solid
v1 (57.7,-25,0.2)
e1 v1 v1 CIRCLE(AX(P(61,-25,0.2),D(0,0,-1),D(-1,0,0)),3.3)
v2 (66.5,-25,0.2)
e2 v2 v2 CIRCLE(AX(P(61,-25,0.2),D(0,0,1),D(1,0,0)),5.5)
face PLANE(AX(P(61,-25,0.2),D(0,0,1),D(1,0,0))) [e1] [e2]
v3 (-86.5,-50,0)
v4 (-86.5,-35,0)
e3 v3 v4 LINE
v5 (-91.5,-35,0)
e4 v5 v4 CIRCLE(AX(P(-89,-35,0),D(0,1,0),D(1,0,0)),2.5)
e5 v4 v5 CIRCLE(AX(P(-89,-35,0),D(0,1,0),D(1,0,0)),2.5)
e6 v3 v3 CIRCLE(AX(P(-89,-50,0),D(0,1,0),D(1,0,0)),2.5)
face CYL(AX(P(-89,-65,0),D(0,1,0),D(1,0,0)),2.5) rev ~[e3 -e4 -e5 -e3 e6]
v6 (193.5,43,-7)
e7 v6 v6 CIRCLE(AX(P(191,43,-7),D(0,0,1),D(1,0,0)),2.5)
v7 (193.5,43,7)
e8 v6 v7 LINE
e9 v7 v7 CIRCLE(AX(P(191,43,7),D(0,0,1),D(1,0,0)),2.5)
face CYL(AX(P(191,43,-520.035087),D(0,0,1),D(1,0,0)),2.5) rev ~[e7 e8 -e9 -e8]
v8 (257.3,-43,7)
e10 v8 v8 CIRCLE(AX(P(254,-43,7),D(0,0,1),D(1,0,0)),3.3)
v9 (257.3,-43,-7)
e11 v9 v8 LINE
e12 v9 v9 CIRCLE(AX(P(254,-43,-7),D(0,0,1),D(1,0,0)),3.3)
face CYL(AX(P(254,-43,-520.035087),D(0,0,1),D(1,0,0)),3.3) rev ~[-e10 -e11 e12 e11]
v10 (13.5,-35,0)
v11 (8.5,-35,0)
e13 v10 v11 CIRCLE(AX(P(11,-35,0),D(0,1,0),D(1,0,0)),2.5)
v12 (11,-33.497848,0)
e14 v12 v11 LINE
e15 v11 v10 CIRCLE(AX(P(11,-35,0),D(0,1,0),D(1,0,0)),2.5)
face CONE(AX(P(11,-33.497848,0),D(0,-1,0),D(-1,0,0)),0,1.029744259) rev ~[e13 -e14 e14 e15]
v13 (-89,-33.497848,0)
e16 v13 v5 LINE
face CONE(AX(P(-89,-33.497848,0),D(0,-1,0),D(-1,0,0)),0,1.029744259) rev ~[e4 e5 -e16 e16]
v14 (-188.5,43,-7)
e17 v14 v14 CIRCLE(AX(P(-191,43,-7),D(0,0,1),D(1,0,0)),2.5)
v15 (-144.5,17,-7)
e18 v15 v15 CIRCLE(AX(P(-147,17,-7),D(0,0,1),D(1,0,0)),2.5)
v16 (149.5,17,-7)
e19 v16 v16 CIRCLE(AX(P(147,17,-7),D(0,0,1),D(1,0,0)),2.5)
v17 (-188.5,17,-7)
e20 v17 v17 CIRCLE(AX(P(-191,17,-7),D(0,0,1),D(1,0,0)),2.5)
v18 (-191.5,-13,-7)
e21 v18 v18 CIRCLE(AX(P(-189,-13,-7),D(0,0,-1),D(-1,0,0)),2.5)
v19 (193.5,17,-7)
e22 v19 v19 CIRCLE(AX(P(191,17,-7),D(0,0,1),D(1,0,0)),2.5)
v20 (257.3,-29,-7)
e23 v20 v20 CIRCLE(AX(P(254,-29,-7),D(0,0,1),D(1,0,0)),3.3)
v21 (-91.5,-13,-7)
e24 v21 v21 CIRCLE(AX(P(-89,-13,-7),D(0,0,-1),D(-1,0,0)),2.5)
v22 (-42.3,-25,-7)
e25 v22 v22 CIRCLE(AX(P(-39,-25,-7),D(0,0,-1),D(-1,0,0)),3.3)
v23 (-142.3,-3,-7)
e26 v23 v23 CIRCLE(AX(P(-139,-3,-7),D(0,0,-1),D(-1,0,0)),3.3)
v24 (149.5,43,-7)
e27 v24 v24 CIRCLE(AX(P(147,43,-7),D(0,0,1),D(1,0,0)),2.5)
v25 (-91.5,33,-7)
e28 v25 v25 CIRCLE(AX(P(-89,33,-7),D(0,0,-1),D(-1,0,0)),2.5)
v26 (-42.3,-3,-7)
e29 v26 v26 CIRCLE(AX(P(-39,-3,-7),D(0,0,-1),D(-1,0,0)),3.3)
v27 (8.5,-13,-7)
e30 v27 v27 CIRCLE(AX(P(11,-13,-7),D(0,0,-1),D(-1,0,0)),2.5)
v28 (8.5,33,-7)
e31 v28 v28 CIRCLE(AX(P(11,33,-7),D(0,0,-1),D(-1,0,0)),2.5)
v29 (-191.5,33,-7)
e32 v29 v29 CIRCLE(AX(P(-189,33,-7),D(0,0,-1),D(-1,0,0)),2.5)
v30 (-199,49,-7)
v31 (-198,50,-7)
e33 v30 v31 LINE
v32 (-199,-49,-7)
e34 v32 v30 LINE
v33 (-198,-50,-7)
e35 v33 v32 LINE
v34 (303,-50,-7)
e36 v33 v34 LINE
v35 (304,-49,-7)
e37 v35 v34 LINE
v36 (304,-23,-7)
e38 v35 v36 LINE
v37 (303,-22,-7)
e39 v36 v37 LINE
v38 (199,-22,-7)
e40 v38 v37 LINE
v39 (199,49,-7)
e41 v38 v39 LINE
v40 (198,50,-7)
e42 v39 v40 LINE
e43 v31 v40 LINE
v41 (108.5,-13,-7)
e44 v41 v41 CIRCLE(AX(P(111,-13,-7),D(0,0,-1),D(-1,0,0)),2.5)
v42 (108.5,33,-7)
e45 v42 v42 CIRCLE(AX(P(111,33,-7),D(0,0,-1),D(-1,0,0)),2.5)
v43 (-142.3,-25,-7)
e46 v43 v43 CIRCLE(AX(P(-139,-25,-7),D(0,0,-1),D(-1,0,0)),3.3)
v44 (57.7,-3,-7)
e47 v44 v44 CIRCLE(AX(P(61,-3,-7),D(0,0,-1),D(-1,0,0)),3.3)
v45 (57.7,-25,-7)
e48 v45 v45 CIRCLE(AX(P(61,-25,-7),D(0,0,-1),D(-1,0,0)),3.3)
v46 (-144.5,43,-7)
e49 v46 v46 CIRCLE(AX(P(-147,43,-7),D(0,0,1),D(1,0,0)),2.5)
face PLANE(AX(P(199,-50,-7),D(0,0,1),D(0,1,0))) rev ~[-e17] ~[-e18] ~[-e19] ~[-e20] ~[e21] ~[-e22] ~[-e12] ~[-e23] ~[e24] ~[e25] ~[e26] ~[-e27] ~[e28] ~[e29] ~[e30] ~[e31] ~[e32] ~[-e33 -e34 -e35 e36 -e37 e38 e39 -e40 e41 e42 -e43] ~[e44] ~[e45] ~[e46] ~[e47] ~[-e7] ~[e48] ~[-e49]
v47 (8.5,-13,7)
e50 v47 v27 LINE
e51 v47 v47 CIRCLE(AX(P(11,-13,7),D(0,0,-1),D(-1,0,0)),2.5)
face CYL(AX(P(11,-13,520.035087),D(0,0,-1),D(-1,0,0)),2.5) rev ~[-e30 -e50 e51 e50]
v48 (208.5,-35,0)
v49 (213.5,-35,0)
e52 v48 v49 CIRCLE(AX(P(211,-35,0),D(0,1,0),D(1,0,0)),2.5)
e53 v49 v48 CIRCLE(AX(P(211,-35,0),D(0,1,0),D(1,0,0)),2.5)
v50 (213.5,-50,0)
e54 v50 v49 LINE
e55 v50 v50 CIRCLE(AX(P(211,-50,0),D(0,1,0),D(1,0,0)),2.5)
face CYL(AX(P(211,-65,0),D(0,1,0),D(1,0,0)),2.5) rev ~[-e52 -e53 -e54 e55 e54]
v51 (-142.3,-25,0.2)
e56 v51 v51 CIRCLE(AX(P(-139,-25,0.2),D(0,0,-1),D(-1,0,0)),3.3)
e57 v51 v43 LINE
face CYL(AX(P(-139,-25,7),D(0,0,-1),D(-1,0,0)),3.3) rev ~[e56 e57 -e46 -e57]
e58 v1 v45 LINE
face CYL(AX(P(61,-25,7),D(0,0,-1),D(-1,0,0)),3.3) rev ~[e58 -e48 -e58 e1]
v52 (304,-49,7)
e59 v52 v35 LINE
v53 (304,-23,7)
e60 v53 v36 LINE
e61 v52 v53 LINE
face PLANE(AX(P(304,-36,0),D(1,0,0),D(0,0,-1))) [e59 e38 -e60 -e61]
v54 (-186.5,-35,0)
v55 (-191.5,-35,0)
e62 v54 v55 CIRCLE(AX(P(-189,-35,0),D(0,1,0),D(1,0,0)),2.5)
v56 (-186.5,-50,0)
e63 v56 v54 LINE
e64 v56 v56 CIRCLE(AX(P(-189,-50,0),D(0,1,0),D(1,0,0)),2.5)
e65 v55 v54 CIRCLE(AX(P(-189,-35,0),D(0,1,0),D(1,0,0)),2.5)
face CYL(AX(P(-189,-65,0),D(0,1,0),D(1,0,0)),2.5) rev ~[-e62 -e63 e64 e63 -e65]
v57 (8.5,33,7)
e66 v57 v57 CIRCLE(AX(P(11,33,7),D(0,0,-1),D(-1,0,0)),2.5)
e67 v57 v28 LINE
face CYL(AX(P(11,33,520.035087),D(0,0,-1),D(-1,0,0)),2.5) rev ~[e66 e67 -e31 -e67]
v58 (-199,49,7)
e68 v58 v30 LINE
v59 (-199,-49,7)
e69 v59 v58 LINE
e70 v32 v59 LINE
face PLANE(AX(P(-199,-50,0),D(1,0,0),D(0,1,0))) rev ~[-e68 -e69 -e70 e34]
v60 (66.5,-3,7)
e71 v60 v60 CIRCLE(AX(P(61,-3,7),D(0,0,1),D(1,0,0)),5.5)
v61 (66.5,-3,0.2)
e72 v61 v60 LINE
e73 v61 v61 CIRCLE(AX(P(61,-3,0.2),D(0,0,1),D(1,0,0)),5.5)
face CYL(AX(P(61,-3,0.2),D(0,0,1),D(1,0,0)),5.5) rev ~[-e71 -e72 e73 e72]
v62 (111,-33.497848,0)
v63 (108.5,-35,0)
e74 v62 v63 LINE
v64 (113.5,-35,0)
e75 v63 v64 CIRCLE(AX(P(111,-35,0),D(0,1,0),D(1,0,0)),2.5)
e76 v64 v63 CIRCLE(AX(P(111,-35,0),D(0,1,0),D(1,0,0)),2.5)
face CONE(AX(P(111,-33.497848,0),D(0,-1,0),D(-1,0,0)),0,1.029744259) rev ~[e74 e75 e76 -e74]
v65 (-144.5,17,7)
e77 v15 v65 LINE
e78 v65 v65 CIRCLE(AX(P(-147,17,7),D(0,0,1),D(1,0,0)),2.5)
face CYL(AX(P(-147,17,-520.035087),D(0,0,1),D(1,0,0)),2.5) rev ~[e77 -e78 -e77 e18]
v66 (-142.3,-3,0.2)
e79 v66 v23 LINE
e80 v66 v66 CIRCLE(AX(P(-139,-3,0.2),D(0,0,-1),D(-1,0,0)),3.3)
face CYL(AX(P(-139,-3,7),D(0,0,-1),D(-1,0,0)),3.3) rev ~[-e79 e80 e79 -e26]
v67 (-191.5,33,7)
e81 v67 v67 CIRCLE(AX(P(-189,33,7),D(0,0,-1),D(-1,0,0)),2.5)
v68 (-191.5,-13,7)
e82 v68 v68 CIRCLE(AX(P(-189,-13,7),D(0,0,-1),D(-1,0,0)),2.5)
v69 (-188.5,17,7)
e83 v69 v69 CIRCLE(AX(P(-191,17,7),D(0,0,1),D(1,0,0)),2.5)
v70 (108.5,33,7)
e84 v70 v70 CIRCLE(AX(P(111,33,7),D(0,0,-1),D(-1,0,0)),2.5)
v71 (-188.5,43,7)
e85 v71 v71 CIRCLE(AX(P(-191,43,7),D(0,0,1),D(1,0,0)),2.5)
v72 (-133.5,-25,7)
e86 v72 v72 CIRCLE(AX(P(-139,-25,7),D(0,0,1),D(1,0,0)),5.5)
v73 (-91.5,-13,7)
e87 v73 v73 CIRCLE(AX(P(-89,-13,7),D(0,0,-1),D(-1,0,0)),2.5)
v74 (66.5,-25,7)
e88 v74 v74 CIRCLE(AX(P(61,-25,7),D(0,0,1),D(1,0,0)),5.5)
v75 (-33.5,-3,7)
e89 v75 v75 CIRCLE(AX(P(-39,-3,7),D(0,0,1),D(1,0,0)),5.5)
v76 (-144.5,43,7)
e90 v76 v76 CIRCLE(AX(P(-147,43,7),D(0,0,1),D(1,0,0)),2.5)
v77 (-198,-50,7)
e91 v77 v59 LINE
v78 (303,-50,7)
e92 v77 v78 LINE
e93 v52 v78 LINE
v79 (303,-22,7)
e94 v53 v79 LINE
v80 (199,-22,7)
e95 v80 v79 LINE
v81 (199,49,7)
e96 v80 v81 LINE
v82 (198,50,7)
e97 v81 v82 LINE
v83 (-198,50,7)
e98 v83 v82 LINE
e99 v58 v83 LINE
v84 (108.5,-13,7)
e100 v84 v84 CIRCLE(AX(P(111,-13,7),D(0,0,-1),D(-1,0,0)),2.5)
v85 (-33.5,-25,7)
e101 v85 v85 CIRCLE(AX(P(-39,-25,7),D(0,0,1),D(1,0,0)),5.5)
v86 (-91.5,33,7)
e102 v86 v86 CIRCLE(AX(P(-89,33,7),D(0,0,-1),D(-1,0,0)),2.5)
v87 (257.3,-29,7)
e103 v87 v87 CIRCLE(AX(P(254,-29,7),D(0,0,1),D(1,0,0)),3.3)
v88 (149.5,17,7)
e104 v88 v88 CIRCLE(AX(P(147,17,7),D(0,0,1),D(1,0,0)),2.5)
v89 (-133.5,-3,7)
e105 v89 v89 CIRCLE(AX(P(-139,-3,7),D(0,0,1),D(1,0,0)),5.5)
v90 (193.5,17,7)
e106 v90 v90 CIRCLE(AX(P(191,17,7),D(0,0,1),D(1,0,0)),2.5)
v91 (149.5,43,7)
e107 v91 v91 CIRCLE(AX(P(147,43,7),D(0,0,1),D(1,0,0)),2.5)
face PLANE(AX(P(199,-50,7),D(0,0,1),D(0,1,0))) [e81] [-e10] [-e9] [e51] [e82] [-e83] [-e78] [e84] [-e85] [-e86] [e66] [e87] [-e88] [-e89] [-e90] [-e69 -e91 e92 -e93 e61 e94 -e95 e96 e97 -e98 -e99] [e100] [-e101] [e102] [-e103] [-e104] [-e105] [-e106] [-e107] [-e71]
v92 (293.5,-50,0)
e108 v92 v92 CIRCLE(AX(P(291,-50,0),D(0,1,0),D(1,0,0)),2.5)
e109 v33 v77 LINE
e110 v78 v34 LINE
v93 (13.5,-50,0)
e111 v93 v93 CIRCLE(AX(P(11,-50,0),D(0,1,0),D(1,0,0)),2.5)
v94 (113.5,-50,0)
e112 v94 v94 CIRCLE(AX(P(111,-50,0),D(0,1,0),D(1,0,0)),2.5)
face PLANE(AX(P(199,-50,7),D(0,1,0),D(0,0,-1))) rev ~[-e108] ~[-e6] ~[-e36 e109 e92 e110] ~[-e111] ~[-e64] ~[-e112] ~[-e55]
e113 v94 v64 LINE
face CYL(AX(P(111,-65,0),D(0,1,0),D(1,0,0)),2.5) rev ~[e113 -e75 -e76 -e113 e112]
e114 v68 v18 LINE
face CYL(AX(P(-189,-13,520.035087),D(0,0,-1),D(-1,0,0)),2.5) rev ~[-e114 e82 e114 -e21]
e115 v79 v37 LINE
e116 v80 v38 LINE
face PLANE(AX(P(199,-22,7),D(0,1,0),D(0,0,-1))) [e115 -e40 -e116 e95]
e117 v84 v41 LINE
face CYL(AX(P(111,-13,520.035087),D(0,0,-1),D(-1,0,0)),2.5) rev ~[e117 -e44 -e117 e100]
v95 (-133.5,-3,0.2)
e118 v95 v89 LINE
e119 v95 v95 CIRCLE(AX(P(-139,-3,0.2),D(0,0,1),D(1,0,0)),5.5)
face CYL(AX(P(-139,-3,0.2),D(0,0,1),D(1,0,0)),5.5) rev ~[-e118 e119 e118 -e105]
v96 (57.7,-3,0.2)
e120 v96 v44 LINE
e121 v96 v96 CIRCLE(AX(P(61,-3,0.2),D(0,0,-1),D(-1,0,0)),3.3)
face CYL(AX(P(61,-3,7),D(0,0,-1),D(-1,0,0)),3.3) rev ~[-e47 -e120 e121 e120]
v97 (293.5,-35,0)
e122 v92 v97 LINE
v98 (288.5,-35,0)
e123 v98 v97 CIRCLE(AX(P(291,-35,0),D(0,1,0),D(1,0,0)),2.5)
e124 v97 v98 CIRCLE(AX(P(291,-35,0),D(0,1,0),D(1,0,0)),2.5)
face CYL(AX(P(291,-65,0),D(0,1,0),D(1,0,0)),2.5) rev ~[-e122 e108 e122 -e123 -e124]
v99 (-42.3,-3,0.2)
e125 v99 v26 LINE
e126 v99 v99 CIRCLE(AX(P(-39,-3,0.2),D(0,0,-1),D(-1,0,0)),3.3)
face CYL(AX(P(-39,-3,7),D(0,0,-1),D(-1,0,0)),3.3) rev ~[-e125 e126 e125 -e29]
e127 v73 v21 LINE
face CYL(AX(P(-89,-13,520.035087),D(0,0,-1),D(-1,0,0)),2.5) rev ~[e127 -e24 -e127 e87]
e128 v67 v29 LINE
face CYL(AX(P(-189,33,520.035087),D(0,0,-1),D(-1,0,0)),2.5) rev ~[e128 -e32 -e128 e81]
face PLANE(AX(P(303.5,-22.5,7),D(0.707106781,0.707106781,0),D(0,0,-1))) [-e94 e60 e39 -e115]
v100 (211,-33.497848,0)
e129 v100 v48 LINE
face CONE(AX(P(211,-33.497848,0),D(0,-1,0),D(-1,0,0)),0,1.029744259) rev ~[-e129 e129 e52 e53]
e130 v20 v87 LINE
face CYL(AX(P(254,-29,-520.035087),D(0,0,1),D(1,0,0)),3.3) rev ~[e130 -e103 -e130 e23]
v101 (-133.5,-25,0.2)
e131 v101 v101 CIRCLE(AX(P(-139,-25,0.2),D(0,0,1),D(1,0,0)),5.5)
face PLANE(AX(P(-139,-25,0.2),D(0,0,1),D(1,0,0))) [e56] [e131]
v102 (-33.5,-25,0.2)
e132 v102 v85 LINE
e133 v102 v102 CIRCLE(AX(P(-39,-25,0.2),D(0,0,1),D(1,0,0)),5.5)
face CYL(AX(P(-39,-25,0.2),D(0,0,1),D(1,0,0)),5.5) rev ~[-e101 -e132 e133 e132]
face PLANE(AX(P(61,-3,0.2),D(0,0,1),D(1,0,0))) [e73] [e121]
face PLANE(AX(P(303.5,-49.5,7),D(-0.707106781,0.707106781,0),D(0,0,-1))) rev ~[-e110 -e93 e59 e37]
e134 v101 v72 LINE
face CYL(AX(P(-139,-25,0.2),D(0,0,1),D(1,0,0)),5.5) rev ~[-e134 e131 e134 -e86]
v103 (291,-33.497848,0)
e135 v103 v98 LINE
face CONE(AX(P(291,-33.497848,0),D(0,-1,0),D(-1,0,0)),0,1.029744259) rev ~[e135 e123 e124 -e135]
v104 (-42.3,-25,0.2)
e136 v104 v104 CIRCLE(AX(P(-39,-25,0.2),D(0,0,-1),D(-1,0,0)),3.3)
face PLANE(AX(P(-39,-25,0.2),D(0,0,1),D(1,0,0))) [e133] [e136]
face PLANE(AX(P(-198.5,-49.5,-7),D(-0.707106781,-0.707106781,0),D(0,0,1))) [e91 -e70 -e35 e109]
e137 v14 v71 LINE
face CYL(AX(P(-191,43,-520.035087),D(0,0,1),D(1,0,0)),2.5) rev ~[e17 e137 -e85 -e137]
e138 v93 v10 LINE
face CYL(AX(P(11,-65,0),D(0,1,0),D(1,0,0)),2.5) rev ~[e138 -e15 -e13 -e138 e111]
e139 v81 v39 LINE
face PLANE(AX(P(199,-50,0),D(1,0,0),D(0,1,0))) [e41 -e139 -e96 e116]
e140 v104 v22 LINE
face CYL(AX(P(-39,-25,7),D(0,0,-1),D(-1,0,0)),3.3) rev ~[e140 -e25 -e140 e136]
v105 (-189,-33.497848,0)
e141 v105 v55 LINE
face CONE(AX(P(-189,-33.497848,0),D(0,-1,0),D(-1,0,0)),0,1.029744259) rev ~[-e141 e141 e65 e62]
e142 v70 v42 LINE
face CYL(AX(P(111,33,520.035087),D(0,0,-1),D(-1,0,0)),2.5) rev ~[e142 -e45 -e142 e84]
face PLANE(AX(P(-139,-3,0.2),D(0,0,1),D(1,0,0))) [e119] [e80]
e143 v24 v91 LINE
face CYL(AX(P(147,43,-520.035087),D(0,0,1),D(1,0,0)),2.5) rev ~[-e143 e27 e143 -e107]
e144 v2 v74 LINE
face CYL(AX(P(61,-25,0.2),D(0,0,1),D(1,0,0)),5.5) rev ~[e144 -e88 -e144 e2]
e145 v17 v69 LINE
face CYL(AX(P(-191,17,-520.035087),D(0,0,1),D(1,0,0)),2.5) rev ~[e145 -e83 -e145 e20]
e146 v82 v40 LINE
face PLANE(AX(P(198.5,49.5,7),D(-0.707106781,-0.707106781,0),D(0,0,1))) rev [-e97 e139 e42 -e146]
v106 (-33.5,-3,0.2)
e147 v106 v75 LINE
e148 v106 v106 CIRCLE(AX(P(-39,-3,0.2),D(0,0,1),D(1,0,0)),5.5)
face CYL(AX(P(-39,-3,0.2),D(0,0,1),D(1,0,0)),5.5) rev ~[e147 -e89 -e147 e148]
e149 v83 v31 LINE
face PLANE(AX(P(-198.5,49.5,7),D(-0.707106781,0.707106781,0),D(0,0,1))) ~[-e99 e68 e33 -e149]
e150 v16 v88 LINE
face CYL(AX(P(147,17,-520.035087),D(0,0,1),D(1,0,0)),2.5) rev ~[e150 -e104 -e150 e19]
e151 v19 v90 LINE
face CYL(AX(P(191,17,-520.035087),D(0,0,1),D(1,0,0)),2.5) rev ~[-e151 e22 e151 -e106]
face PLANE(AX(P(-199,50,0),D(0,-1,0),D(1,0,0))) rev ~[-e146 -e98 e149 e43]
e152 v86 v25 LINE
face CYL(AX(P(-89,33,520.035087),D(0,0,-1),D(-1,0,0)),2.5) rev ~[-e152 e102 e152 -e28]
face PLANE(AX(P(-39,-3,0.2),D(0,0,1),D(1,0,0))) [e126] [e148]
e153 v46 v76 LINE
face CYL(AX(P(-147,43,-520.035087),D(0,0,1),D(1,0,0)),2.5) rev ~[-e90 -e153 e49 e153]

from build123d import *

# Parameters (mm, degrees)
SKETCH1_W                                            = 398
SKETCH1_H                                            = 100
BOSS_EXTRUDE1_DEPTH                                  = 7
SKETCH2_W                                            = 14
SKETCH2_H                                            = 28
BOSS_EXTRUDE2_DEPTH                                  = 105
M6_CLEARANCE_HOLE1_D                                 = 6.6
M6_TAPPED_HOLE1_D                                    = 5
HOLE_SIZE_PER_SOCKET_HEAD_CAP_SCREW_TYPE_D           = 6.6
HOLE_SIZE_PER_SOCKET_HEAD_CAP_SCREW_TYPE_CBORE_D     = 11
HOLE_SIZE_PER_SOCKET_HEAD_CAP_SCREW_TYPE_CBORE_DEPTH = 6.8
M6_TAPPED_HOLE2_D                                    = 5
M6_TAPPED_HOLE3_D                                    = 5
M6_TAPPED_HOLE3_DEPTH                                = 15
M6_TAPPED_HOLE3_TIP                                  = 1.502151548
CHAMFER1_SIZE                                        = 1


with BuildPart() as part:
    # Sketch1 → Boss-Extrude1 (new, symmetric)
    with BuildSketch(Plane.XY):
        Rectangle(SKETCH1_W, SKETCH1_H)
    extrude(amount=BOSS_EXTRUDE1_DEPTH, both=True)

    # Sketch2 → Boss-Extrude2 (add)
    with BuildSketch(Plane(origin=(199, 0, 0), x_dir=(0, 0, -1), z_dir=(1, 0, 0))):
        with Locations((0, -36)):
            Rectangle(SKETCH2_W, SKETCH2_H)
    extrude(amount=BOSS_EXTRUDE2_DEPTH)

    # M6 Clearance Hole1 (through all)
    with Locations(Plane(origin=(0, 0, -7), x_dir=(-1, 0, 0), z_dir=(0, 0, -1))):
        with Locations((-254, -43), (-254, -29)):
            Hole(M6_CLEARANCE_HOLE1_D / 2)

    # M6 Tapped Hole1 (through all)
    with Locations(Plane.XY.offset(7)):
        with Locations((111, -13), (-189, 33), (-189, -13), (-89, 33), (-89, -13), (11, 33), (11, -13), (111, 33)):
            Hole(M6_TAPPED_HOLE1_D / 2)

    # Hole Size per Socket Head Cap Screw Type1 (through all)
    with Locations(Plane.XY.offset(7)):
        with Locations((-139, -3), (61, -25), (61, -3), (-39, -25), (-39, -3), (-139, -25)):
            CounterBoreHole(HOLE_SIZE_PER_SOCKET_HEAD_CAP_SCREW_TYPE_D / 2, HOLE_SIZE_PER_SOCKET_HEAD_CAP_SCREW_TYPE_CBORE_D / 2, HOLE_SIZE_PER_SOCKET_HEAD_CAP_SCREW_TYPE_CBORE_DEPTH)

    # M6 Tapped Hole2 (through all)
    with Locations(Plane(origin=(0, 0, -7), x_dir=(-1, 0, 0), z_dir=(0, 0, -1))):
        with Locations((-191, 43), (-147, 17), (-191, 17), (-147, 43), (147, 43), (191, 17), (147, 17), (191, 43)):
            Hole(M6_TAPPED_HOLE2_D / 2)

    # M6 Tapped Hole3
    with Locations(Plane(origin=(0, -50, 0), x_dir=(-1, 0, 0), z_dir=(0, -1, 0))):
        with Locations((-291, 0), (189, 0), (89, 0), (-11, 0), (-111, 0), (-211, 0)):
            Hole(M6_TAPPED_HOLE3_D / 2, depth=M6_TAPPED_HOLE3_DEPTH)
            with Locations((0, 0, -(M6_TAPPED_HOLE3_DEPTH + M6_TAPPED_HOLE3_TIP / 2))):  # 118° drill point
                Cone(0, M6_TAPPED_HOLE3_D / 2, M6_TAPPED_HOLE3_TIP, mode=Mode.SUBTRACT)

    # Chamfer1
    chamfer1_edges = [part.edges().sort_by_distance(p)[0] for p in [
        (304, -50, 0),
        (304, -22, 0),
        (-199, -50, 0),
        (-199, 50, 0),
        (199, 50, 0),
    ]]
    chamfer(chamfer1_edges, length=CHAMFER1_SIZE)


solid = part.part
